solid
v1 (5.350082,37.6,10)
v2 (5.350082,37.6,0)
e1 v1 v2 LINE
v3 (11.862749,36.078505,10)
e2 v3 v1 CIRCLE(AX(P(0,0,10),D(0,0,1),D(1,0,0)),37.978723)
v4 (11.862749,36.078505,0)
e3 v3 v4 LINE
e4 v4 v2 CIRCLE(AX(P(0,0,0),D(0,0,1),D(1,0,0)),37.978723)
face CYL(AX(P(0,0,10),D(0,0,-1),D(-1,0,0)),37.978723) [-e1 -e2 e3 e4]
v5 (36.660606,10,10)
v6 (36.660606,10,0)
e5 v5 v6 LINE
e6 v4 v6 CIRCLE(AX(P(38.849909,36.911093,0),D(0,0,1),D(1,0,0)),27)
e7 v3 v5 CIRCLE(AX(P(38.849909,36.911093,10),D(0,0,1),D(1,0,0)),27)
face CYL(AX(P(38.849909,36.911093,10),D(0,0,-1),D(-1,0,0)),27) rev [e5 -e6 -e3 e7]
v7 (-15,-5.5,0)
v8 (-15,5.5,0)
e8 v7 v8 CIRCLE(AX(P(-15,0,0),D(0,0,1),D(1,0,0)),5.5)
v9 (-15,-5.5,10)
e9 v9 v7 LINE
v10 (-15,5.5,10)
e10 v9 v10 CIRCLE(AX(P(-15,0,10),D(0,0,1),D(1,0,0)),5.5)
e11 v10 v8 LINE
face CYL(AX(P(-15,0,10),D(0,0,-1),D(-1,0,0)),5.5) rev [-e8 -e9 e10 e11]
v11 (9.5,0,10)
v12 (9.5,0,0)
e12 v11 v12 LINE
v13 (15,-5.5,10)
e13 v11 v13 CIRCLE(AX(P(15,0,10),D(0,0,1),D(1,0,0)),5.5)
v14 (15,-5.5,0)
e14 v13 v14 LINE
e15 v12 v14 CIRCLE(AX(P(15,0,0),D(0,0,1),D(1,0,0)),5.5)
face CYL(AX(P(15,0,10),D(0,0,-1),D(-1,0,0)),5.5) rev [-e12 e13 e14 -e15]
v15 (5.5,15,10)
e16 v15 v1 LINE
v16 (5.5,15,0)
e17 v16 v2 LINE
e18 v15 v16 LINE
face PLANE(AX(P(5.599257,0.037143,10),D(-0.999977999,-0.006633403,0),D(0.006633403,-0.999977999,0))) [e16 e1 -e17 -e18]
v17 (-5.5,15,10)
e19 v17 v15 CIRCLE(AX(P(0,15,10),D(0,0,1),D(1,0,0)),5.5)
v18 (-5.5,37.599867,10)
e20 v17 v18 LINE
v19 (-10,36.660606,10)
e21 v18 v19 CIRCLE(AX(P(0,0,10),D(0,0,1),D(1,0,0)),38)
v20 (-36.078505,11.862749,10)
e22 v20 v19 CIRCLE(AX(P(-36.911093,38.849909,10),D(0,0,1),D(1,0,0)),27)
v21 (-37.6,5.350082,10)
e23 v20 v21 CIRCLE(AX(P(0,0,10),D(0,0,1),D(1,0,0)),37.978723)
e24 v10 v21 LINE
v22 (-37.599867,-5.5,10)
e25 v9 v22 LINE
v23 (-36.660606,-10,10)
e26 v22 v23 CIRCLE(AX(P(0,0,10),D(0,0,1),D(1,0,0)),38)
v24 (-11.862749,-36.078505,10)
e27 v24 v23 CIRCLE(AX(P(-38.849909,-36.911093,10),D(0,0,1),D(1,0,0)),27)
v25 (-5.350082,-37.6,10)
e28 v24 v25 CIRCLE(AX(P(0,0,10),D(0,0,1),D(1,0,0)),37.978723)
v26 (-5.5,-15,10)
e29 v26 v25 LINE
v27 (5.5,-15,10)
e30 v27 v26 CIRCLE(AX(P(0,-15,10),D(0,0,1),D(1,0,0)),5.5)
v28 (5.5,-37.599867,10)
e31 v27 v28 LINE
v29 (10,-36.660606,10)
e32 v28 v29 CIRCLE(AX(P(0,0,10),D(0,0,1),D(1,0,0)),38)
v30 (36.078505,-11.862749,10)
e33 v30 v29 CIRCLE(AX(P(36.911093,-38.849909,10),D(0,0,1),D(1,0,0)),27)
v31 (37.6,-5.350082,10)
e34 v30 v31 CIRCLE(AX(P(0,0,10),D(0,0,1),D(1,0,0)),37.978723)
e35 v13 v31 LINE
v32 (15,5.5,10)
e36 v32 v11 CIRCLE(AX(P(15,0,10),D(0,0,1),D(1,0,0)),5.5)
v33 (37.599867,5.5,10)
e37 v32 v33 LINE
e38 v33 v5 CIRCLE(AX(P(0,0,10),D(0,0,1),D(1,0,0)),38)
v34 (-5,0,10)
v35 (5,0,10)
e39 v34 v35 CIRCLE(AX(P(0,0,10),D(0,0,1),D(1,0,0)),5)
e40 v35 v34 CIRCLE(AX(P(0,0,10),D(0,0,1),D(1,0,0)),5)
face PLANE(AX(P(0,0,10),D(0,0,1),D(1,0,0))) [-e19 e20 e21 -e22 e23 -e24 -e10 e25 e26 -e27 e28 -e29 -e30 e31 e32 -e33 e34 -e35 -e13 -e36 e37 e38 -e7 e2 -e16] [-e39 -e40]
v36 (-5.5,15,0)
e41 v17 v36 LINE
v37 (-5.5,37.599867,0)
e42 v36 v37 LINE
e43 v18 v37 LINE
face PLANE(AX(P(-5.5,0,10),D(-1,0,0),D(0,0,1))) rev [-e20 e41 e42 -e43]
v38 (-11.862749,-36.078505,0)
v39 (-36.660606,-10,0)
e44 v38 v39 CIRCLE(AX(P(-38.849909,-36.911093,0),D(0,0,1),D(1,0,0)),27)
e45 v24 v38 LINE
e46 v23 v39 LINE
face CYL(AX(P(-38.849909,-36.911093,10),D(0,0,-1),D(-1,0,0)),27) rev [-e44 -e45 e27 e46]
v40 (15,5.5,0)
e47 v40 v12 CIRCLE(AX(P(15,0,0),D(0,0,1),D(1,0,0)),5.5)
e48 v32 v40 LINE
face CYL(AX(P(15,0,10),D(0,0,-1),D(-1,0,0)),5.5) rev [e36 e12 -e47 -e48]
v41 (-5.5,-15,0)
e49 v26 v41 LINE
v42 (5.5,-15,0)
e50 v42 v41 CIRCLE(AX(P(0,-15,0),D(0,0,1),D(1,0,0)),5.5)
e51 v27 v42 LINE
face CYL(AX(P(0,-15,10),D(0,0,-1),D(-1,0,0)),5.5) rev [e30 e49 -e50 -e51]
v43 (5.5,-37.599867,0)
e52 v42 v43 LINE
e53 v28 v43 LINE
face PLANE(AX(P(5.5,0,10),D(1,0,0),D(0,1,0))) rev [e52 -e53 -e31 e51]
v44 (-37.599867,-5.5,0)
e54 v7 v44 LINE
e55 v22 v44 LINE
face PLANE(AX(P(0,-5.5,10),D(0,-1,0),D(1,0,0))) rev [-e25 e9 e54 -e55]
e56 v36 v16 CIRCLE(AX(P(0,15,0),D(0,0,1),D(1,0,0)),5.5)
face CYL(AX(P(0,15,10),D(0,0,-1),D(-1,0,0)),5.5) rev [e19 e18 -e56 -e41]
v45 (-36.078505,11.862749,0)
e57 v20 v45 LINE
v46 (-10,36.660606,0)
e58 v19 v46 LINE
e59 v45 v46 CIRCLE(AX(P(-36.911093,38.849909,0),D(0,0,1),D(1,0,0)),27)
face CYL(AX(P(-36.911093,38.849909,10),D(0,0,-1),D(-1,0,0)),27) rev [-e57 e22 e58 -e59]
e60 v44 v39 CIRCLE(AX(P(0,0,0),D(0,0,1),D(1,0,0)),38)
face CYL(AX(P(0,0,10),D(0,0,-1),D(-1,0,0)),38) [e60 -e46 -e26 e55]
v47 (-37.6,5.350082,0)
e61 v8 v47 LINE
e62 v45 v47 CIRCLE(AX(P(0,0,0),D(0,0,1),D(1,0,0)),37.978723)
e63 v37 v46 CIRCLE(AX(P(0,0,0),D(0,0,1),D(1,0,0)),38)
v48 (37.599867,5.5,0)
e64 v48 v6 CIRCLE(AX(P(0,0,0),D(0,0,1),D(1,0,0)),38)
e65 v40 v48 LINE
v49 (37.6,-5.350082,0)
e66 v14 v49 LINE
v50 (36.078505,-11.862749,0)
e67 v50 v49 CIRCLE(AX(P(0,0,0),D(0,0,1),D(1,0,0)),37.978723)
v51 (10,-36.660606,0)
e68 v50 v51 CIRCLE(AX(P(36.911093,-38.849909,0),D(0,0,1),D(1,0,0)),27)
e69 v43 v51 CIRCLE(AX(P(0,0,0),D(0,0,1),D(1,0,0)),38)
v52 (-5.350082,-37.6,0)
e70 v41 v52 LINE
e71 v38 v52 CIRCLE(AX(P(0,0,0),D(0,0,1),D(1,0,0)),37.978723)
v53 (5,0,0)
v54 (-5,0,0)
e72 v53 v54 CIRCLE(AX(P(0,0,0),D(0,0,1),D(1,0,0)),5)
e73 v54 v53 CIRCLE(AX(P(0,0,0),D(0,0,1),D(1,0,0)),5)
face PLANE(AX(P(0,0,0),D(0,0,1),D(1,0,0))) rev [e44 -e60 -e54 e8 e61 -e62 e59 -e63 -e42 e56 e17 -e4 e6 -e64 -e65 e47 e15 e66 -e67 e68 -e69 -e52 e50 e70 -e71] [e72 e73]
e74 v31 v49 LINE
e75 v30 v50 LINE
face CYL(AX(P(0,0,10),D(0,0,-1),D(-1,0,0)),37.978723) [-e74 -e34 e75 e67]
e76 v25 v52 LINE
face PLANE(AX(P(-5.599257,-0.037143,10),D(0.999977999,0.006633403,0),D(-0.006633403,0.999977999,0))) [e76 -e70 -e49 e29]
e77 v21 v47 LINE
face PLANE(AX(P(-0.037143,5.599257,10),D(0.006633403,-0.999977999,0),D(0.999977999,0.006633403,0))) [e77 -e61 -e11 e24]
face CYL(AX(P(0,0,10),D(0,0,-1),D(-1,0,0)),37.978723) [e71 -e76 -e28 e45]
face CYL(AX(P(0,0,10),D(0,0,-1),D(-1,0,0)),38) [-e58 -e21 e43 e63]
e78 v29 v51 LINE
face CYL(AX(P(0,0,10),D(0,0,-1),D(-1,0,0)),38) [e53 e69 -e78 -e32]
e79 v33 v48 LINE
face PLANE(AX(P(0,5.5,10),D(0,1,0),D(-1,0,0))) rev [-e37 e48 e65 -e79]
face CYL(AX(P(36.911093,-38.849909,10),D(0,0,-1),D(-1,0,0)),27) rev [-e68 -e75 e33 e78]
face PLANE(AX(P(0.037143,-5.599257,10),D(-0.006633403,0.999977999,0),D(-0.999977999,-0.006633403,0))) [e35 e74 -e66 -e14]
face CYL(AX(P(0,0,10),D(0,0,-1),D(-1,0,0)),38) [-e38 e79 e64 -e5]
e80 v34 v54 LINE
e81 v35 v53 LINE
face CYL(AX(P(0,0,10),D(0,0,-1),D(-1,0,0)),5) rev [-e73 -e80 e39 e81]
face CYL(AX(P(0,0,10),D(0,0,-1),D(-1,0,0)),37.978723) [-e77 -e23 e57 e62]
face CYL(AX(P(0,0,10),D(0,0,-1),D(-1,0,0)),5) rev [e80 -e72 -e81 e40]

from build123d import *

# Parameters (mm, degrees)
GENEVA_WHEEL_PROFILE_R       = 5
GENEVA_WHEEL_BODY_10MM_DEPTH = 10


with BuildPart() as part:
    # Geneva Wheel Profile → Geneva Wheel Body 10mm (new body)
    with BuildSketch(Plane.XY):
        with BuildLine():
            ThreePointArc((-36.078505425, 11.862749321), (-18.305680685, 19.283646977), (-10, 36.66060556))
            ThreePointArc((-10, 36.66060556), (-7.764216189, 37.198346025), (-5.5, 37.599867021))
            Line((-5.5, 37.599867021), (-5.5, 15))
            ThreePointArc((-5.5, 15), (0, 9.5), (5.5, 15))
            Line((5.5, 15), (5.350081788, 37.6))
            ThreePointArc((5.350081788, 37.6), (8.639972519, 36.982891315), (11.862749321, 36.078505425))
            ThreePointArc((11.862749321, 36.078505425), (19.283646977, 18.305680685), (36.66060556, 10))
            ThreePointArc((36.66060556, 10), (37.198346025, 7.764216189), (37.599867021, 5.5))
            Line((37.599867021, 5.5), (15, 5.5))
            ThreePointArc((15, 5.5), (9.5, 0), (15, -5.5))
            Line((15, -5.5), (37.6, -5.350081788))
            ThreePointArc((37.6, -5.350081788), (36.982891315, -8.639972519), (36.078505425, -11.862749321))
            ThreePointArc((36.078505425, -11.862749321), (18.305680685, -19.283646977), (10, -36.66060556))
            ThreePointArc((10, -36.66060556), (7.764216189, -37.198346025), (5.5, -37.599867021))
            Line((5.5, -37.599867021), (5.5, -15))
            ThreePointArc((5.5, -15), (0, -9.5), (-5.5, -15))
            Line((-5.5, -15), (-5.350081788, -37.6))
            ThreePointArc((-5.350081788, -37.6), (-8.639972519, -36.982891315), (-11.862749321, -36.078505425))
            ThreePointArc((-11.862749321, -36.078505425), (-19.283646977, -18.305680685), (-36.66060556, -10))
            ThreePointArc((-36.66060556, -10), (-37.198346025, -7.764216189), (-37.599867021, -5.5))
            Line((-37.599867021, -5.5), (-15, -5.5))
            ThreePointArc((-15, -5.5), (-9.5, 0), (-15, 5.5))
            Line((-15, 5.5), (-37.6, 5.350081788))
            ThreePointArc((-37.6, 5.350081788), (-36.982891315, 8.639972519), (-36.078505425, 11.862749321))
        make_face()
        Circle(GENEVA_WHEEL_PROFILE_R, mode=Mode.SUBTRACT)
    extrude(amount=GENEVA_WHEEL_BODY_10MM_DEPTH)


solid = part.part
